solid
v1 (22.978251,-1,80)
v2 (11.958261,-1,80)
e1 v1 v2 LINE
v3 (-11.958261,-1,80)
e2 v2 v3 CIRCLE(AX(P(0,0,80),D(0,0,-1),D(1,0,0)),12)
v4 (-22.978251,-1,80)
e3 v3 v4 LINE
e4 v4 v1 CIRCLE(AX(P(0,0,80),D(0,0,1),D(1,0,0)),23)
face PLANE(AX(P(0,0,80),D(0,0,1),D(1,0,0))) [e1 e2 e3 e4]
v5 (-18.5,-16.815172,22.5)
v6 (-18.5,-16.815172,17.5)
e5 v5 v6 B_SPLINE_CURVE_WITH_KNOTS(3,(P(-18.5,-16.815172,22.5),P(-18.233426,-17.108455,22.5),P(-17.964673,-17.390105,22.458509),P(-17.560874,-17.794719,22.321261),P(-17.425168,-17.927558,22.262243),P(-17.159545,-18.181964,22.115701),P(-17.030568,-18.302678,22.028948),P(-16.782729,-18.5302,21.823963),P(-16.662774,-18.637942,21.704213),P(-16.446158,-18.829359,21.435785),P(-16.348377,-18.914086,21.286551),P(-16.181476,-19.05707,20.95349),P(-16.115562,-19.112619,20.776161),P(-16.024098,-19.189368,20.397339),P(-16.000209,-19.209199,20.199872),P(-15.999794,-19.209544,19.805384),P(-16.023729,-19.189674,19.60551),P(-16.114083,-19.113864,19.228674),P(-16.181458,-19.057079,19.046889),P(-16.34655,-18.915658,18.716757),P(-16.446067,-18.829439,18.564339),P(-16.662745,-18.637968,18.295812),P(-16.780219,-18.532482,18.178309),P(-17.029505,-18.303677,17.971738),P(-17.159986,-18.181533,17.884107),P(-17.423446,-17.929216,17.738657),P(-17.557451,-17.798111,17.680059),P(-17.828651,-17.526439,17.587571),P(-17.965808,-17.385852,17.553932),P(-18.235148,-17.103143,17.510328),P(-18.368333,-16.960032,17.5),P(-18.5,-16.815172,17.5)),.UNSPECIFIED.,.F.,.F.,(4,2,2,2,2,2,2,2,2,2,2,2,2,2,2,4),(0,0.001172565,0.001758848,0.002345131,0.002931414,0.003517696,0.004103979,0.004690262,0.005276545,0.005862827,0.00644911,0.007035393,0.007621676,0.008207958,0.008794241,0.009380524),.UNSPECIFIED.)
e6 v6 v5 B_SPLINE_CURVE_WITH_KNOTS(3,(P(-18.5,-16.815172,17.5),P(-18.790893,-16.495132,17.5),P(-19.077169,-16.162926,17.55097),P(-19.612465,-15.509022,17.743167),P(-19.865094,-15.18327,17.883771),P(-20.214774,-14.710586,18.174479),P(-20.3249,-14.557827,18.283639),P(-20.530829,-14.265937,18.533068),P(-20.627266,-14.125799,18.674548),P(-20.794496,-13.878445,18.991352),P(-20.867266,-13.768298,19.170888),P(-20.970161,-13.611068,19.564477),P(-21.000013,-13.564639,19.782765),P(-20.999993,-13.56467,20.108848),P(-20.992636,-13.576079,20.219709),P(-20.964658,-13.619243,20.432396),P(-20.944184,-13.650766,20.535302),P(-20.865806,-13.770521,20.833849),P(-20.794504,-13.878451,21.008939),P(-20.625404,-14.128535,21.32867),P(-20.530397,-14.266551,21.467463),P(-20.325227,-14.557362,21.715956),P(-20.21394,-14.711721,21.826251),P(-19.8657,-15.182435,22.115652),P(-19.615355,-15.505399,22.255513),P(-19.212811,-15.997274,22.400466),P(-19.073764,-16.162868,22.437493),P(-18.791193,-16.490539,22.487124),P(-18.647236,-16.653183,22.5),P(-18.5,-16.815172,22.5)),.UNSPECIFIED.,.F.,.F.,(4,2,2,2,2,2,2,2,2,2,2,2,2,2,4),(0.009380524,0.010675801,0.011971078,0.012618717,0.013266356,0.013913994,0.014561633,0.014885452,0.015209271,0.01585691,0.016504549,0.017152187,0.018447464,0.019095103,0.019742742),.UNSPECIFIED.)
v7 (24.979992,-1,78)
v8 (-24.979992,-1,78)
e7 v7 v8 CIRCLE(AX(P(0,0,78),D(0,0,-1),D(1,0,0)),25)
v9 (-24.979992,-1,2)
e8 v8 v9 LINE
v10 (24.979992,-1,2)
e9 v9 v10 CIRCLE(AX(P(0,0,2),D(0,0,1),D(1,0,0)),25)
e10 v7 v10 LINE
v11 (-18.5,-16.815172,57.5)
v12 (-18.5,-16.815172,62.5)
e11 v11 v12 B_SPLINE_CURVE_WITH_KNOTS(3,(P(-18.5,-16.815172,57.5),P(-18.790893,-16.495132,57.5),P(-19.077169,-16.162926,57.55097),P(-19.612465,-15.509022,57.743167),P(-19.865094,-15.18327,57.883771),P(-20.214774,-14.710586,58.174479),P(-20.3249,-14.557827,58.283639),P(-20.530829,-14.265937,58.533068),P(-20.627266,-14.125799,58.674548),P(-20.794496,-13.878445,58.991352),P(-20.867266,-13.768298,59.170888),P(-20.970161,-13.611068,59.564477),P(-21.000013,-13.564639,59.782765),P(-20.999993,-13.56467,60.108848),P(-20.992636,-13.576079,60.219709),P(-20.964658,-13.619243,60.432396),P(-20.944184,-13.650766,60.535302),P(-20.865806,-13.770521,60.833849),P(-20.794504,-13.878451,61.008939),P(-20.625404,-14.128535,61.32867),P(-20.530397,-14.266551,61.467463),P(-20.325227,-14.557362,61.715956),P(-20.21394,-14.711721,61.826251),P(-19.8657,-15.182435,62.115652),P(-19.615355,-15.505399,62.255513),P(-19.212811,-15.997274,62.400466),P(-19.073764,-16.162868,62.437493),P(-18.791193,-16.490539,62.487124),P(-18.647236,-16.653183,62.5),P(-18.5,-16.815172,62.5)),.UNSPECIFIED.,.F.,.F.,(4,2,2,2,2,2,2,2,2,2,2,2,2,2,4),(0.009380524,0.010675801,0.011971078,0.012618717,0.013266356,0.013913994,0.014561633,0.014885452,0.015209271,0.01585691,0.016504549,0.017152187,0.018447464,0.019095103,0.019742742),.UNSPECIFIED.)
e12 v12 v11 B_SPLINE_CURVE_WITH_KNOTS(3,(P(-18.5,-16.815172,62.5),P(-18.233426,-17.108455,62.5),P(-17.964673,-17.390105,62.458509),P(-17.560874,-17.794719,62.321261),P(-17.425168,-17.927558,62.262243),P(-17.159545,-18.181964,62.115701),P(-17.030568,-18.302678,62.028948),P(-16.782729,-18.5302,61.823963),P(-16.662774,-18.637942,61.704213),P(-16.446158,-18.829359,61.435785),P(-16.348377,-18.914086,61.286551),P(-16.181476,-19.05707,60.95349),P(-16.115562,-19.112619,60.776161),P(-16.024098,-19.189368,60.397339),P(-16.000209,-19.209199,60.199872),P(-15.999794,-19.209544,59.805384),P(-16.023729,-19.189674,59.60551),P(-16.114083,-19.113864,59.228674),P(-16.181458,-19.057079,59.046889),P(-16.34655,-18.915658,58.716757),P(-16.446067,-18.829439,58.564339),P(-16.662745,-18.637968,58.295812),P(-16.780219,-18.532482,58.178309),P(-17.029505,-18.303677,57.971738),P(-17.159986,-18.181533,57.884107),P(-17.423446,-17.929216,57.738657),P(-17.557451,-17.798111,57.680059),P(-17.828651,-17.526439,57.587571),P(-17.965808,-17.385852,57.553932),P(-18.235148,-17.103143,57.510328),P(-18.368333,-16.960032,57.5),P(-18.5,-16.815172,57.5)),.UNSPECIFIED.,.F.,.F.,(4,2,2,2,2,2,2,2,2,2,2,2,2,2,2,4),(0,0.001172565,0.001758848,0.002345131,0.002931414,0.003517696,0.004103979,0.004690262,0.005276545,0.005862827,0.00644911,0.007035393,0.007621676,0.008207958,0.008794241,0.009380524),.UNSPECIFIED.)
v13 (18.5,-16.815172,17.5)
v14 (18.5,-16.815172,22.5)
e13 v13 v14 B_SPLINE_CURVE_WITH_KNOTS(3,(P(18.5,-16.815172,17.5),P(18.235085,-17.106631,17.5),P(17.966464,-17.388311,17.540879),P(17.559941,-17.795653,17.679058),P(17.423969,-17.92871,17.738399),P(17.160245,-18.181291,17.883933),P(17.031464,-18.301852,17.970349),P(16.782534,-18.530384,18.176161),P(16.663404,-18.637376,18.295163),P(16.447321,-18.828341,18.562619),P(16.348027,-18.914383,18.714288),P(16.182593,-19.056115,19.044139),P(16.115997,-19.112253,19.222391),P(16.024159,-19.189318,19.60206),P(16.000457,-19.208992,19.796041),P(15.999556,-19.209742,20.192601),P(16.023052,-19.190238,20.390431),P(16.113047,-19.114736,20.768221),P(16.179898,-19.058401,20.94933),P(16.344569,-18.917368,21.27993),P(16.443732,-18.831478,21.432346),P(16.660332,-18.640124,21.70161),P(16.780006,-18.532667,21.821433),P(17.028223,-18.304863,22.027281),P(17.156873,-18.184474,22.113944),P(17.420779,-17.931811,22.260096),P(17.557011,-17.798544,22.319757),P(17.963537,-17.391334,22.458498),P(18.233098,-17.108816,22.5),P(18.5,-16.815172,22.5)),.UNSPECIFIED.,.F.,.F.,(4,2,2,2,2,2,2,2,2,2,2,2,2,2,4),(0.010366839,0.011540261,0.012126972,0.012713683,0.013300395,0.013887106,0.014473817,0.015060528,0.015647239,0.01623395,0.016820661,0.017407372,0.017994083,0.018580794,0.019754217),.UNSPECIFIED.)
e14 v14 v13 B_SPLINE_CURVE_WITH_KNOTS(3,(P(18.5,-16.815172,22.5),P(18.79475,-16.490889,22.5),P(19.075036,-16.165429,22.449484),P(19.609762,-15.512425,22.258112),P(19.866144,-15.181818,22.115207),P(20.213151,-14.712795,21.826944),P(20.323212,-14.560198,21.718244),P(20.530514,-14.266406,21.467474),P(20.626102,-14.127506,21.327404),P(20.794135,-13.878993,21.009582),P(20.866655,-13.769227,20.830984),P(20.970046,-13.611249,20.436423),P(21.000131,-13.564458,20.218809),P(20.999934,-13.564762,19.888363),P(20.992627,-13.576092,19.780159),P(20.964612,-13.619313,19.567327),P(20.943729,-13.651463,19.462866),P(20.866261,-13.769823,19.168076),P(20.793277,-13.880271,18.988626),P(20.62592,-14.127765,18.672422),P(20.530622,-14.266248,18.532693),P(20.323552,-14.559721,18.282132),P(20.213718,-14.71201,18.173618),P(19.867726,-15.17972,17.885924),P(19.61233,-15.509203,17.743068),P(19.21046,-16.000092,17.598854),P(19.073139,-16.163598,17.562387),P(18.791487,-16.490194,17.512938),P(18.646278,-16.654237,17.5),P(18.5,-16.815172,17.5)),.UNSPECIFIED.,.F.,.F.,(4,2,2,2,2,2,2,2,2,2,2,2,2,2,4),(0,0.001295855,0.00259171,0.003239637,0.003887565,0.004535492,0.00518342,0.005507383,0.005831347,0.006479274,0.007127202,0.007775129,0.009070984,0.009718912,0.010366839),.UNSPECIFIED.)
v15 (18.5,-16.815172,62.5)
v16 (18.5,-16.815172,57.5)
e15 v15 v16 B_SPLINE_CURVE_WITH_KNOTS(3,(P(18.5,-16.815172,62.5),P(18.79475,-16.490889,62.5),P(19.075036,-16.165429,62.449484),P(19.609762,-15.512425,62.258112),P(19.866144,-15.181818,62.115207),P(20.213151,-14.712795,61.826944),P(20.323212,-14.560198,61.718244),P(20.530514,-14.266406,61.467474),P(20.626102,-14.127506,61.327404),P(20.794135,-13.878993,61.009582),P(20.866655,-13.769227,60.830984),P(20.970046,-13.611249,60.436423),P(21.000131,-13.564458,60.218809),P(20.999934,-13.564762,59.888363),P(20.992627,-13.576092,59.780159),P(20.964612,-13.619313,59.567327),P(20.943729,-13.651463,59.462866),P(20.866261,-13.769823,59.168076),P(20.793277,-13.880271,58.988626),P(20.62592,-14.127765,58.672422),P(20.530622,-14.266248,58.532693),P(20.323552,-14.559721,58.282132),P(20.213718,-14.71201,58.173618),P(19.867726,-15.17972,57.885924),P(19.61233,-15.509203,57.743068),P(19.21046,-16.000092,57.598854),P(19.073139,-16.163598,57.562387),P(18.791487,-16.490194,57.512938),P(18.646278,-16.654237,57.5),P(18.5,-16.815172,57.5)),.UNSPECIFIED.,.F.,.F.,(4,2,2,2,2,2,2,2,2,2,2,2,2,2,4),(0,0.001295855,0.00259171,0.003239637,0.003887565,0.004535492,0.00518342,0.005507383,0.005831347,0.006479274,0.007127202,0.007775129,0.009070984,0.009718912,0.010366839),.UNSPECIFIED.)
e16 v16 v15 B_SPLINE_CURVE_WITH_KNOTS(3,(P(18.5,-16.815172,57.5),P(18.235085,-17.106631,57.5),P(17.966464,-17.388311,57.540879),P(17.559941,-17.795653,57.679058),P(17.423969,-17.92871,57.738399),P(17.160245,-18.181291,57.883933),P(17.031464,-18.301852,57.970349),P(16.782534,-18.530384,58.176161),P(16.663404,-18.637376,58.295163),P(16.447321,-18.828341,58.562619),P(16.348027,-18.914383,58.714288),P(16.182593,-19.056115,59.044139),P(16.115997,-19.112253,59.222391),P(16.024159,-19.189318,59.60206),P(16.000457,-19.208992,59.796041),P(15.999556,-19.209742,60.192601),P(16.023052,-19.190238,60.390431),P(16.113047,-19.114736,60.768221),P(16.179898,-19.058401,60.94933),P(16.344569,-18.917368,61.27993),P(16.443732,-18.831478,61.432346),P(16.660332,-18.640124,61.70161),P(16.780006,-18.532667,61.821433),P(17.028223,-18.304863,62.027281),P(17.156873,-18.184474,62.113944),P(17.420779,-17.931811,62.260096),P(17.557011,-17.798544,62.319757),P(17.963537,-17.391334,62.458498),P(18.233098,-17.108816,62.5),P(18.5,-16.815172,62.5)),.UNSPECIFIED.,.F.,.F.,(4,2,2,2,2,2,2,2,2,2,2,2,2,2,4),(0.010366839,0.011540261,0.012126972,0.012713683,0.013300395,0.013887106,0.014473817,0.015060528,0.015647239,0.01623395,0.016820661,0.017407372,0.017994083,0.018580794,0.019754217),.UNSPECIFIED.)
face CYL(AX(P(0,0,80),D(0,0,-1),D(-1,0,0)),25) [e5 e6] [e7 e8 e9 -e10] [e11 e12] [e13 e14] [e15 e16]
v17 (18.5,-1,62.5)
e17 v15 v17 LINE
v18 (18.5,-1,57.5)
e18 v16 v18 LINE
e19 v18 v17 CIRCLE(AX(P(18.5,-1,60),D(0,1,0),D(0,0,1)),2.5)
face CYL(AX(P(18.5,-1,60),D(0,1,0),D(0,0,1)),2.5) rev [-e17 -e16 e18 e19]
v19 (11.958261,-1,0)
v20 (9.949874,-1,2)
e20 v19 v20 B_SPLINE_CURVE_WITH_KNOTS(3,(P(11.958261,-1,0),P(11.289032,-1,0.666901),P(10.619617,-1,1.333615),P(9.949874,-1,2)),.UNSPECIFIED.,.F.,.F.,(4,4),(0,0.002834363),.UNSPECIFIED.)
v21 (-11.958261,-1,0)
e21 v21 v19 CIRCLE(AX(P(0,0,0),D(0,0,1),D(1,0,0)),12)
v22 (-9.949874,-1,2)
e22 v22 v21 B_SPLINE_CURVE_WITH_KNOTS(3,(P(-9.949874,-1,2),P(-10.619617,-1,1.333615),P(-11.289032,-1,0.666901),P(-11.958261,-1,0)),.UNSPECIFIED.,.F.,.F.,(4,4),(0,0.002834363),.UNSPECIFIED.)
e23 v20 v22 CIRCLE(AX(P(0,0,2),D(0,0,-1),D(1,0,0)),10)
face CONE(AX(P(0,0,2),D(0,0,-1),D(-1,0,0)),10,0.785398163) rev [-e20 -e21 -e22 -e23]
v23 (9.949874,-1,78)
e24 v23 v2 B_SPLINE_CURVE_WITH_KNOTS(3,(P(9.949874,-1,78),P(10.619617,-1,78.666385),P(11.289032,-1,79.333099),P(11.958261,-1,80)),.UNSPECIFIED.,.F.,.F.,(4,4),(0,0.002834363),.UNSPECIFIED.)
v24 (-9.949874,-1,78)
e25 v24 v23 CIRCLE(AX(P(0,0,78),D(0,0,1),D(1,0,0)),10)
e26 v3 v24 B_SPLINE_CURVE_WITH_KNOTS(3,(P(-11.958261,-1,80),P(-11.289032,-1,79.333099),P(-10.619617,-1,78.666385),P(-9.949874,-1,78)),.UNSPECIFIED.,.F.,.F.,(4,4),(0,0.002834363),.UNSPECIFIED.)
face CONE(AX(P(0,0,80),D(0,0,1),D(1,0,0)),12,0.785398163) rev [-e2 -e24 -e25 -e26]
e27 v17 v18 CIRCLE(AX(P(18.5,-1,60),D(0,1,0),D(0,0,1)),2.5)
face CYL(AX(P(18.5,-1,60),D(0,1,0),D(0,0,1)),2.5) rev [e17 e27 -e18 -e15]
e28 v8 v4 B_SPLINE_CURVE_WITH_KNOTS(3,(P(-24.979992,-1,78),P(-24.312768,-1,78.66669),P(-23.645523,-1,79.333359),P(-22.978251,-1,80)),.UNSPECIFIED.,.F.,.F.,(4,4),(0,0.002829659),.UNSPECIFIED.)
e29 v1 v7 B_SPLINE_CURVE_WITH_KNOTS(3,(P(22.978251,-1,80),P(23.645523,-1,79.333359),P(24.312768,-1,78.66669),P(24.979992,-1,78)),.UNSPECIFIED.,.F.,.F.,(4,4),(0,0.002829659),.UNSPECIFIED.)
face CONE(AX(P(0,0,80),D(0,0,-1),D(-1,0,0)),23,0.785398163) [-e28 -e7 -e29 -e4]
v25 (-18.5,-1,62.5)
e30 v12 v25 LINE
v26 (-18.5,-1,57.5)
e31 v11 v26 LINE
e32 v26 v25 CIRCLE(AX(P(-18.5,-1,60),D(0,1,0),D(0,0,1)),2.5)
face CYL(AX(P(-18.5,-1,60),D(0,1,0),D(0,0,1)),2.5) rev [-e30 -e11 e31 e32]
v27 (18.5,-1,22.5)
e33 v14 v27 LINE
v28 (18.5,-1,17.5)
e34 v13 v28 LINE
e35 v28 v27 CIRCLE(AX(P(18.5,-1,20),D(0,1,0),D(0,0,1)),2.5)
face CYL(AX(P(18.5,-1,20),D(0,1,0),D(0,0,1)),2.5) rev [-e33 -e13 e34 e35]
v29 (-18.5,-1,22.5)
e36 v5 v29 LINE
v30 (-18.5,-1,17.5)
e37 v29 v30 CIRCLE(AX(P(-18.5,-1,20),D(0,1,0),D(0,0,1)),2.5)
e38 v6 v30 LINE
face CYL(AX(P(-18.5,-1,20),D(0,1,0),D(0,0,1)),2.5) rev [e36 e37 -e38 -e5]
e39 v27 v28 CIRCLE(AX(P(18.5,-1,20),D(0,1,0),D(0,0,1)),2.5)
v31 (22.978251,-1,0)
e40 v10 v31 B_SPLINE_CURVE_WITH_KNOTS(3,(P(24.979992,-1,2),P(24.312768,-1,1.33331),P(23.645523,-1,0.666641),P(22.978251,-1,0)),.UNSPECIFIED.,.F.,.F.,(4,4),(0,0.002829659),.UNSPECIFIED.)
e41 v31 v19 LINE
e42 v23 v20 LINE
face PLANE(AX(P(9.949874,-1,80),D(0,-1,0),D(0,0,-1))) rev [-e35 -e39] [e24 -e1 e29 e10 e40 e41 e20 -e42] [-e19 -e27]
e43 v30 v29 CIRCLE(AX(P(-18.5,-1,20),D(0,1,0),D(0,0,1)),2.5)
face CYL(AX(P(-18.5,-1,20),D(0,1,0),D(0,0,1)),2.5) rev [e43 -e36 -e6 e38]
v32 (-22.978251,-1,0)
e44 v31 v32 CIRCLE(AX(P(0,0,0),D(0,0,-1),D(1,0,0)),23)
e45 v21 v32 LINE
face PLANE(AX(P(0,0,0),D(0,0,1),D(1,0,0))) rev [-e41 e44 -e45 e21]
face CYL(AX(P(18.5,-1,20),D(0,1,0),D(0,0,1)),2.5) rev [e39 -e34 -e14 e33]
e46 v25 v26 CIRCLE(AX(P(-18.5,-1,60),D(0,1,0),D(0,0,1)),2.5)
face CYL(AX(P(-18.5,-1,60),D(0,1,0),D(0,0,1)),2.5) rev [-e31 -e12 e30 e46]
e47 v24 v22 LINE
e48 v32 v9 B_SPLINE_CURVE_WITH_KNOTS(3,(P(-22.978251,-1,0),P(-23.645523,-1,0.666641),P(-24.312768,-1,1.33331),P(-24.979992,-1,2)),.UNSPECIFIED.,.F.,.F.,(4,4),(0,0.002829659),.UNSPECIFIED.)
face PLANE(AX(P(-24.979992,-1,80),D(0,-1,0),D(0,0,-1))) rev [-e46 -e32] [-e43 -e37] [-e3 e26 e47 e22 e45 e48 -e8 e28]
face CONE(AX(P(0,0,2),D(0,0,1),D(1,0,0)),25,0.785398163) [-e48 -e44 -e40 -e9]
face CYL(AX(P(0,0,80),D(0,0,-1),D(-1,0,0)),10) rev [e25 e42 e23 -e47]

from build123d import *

# Parameters (mm, degrees)
EXTRUDE_1_DEPTH    = 80
HOLE_WIZARD_M6_1_D = 5
CHAMFER_1_SIZE     = 2


with BuildPart() as part:
    # 草图1 → 凸台-拉伸1 (new body)
    with BuildSketch(Plane.XY):
        with BuildLine():
            Line((-24.979991994, -1), (-9.949874371, -1))
            ThreePointArc((-9.949874371, -1), (0, -10), (9.949874371, -1))
            Line((9.949874371, -1), (24.979991994, -1))
            ThreePointArc((24.979991994, -1), (0, -25), (-24.979991994, -1))
        make_face()
    extrude(amount=EXTRUDE_1_DEPTH)

    # M6 螺纹孔1 (through all)
    with Locations(Plane(origin=(0, -1, 0), x_dir=(1, 0, 0), z_dir=(0, 1, 0))):
        with Locations((-18.5, -20), (18.5, -20), (18.5, -60), (-18.5, -60)):
            Hole(HOLE_WIZARD_M6_1_D / 2)

    # 倒角1
    chamfer_1_edges = [part.edges().sort_by_distance(p)[0] for p in [
        (0, -25, 80),
        (0, -10, 80),
        (0, -25, 0),
        (0, -10, 0),
    ]]
    chamfer(chamfer_1_edges, length=CHAMFER_1_SIZE)


solid = part.part
